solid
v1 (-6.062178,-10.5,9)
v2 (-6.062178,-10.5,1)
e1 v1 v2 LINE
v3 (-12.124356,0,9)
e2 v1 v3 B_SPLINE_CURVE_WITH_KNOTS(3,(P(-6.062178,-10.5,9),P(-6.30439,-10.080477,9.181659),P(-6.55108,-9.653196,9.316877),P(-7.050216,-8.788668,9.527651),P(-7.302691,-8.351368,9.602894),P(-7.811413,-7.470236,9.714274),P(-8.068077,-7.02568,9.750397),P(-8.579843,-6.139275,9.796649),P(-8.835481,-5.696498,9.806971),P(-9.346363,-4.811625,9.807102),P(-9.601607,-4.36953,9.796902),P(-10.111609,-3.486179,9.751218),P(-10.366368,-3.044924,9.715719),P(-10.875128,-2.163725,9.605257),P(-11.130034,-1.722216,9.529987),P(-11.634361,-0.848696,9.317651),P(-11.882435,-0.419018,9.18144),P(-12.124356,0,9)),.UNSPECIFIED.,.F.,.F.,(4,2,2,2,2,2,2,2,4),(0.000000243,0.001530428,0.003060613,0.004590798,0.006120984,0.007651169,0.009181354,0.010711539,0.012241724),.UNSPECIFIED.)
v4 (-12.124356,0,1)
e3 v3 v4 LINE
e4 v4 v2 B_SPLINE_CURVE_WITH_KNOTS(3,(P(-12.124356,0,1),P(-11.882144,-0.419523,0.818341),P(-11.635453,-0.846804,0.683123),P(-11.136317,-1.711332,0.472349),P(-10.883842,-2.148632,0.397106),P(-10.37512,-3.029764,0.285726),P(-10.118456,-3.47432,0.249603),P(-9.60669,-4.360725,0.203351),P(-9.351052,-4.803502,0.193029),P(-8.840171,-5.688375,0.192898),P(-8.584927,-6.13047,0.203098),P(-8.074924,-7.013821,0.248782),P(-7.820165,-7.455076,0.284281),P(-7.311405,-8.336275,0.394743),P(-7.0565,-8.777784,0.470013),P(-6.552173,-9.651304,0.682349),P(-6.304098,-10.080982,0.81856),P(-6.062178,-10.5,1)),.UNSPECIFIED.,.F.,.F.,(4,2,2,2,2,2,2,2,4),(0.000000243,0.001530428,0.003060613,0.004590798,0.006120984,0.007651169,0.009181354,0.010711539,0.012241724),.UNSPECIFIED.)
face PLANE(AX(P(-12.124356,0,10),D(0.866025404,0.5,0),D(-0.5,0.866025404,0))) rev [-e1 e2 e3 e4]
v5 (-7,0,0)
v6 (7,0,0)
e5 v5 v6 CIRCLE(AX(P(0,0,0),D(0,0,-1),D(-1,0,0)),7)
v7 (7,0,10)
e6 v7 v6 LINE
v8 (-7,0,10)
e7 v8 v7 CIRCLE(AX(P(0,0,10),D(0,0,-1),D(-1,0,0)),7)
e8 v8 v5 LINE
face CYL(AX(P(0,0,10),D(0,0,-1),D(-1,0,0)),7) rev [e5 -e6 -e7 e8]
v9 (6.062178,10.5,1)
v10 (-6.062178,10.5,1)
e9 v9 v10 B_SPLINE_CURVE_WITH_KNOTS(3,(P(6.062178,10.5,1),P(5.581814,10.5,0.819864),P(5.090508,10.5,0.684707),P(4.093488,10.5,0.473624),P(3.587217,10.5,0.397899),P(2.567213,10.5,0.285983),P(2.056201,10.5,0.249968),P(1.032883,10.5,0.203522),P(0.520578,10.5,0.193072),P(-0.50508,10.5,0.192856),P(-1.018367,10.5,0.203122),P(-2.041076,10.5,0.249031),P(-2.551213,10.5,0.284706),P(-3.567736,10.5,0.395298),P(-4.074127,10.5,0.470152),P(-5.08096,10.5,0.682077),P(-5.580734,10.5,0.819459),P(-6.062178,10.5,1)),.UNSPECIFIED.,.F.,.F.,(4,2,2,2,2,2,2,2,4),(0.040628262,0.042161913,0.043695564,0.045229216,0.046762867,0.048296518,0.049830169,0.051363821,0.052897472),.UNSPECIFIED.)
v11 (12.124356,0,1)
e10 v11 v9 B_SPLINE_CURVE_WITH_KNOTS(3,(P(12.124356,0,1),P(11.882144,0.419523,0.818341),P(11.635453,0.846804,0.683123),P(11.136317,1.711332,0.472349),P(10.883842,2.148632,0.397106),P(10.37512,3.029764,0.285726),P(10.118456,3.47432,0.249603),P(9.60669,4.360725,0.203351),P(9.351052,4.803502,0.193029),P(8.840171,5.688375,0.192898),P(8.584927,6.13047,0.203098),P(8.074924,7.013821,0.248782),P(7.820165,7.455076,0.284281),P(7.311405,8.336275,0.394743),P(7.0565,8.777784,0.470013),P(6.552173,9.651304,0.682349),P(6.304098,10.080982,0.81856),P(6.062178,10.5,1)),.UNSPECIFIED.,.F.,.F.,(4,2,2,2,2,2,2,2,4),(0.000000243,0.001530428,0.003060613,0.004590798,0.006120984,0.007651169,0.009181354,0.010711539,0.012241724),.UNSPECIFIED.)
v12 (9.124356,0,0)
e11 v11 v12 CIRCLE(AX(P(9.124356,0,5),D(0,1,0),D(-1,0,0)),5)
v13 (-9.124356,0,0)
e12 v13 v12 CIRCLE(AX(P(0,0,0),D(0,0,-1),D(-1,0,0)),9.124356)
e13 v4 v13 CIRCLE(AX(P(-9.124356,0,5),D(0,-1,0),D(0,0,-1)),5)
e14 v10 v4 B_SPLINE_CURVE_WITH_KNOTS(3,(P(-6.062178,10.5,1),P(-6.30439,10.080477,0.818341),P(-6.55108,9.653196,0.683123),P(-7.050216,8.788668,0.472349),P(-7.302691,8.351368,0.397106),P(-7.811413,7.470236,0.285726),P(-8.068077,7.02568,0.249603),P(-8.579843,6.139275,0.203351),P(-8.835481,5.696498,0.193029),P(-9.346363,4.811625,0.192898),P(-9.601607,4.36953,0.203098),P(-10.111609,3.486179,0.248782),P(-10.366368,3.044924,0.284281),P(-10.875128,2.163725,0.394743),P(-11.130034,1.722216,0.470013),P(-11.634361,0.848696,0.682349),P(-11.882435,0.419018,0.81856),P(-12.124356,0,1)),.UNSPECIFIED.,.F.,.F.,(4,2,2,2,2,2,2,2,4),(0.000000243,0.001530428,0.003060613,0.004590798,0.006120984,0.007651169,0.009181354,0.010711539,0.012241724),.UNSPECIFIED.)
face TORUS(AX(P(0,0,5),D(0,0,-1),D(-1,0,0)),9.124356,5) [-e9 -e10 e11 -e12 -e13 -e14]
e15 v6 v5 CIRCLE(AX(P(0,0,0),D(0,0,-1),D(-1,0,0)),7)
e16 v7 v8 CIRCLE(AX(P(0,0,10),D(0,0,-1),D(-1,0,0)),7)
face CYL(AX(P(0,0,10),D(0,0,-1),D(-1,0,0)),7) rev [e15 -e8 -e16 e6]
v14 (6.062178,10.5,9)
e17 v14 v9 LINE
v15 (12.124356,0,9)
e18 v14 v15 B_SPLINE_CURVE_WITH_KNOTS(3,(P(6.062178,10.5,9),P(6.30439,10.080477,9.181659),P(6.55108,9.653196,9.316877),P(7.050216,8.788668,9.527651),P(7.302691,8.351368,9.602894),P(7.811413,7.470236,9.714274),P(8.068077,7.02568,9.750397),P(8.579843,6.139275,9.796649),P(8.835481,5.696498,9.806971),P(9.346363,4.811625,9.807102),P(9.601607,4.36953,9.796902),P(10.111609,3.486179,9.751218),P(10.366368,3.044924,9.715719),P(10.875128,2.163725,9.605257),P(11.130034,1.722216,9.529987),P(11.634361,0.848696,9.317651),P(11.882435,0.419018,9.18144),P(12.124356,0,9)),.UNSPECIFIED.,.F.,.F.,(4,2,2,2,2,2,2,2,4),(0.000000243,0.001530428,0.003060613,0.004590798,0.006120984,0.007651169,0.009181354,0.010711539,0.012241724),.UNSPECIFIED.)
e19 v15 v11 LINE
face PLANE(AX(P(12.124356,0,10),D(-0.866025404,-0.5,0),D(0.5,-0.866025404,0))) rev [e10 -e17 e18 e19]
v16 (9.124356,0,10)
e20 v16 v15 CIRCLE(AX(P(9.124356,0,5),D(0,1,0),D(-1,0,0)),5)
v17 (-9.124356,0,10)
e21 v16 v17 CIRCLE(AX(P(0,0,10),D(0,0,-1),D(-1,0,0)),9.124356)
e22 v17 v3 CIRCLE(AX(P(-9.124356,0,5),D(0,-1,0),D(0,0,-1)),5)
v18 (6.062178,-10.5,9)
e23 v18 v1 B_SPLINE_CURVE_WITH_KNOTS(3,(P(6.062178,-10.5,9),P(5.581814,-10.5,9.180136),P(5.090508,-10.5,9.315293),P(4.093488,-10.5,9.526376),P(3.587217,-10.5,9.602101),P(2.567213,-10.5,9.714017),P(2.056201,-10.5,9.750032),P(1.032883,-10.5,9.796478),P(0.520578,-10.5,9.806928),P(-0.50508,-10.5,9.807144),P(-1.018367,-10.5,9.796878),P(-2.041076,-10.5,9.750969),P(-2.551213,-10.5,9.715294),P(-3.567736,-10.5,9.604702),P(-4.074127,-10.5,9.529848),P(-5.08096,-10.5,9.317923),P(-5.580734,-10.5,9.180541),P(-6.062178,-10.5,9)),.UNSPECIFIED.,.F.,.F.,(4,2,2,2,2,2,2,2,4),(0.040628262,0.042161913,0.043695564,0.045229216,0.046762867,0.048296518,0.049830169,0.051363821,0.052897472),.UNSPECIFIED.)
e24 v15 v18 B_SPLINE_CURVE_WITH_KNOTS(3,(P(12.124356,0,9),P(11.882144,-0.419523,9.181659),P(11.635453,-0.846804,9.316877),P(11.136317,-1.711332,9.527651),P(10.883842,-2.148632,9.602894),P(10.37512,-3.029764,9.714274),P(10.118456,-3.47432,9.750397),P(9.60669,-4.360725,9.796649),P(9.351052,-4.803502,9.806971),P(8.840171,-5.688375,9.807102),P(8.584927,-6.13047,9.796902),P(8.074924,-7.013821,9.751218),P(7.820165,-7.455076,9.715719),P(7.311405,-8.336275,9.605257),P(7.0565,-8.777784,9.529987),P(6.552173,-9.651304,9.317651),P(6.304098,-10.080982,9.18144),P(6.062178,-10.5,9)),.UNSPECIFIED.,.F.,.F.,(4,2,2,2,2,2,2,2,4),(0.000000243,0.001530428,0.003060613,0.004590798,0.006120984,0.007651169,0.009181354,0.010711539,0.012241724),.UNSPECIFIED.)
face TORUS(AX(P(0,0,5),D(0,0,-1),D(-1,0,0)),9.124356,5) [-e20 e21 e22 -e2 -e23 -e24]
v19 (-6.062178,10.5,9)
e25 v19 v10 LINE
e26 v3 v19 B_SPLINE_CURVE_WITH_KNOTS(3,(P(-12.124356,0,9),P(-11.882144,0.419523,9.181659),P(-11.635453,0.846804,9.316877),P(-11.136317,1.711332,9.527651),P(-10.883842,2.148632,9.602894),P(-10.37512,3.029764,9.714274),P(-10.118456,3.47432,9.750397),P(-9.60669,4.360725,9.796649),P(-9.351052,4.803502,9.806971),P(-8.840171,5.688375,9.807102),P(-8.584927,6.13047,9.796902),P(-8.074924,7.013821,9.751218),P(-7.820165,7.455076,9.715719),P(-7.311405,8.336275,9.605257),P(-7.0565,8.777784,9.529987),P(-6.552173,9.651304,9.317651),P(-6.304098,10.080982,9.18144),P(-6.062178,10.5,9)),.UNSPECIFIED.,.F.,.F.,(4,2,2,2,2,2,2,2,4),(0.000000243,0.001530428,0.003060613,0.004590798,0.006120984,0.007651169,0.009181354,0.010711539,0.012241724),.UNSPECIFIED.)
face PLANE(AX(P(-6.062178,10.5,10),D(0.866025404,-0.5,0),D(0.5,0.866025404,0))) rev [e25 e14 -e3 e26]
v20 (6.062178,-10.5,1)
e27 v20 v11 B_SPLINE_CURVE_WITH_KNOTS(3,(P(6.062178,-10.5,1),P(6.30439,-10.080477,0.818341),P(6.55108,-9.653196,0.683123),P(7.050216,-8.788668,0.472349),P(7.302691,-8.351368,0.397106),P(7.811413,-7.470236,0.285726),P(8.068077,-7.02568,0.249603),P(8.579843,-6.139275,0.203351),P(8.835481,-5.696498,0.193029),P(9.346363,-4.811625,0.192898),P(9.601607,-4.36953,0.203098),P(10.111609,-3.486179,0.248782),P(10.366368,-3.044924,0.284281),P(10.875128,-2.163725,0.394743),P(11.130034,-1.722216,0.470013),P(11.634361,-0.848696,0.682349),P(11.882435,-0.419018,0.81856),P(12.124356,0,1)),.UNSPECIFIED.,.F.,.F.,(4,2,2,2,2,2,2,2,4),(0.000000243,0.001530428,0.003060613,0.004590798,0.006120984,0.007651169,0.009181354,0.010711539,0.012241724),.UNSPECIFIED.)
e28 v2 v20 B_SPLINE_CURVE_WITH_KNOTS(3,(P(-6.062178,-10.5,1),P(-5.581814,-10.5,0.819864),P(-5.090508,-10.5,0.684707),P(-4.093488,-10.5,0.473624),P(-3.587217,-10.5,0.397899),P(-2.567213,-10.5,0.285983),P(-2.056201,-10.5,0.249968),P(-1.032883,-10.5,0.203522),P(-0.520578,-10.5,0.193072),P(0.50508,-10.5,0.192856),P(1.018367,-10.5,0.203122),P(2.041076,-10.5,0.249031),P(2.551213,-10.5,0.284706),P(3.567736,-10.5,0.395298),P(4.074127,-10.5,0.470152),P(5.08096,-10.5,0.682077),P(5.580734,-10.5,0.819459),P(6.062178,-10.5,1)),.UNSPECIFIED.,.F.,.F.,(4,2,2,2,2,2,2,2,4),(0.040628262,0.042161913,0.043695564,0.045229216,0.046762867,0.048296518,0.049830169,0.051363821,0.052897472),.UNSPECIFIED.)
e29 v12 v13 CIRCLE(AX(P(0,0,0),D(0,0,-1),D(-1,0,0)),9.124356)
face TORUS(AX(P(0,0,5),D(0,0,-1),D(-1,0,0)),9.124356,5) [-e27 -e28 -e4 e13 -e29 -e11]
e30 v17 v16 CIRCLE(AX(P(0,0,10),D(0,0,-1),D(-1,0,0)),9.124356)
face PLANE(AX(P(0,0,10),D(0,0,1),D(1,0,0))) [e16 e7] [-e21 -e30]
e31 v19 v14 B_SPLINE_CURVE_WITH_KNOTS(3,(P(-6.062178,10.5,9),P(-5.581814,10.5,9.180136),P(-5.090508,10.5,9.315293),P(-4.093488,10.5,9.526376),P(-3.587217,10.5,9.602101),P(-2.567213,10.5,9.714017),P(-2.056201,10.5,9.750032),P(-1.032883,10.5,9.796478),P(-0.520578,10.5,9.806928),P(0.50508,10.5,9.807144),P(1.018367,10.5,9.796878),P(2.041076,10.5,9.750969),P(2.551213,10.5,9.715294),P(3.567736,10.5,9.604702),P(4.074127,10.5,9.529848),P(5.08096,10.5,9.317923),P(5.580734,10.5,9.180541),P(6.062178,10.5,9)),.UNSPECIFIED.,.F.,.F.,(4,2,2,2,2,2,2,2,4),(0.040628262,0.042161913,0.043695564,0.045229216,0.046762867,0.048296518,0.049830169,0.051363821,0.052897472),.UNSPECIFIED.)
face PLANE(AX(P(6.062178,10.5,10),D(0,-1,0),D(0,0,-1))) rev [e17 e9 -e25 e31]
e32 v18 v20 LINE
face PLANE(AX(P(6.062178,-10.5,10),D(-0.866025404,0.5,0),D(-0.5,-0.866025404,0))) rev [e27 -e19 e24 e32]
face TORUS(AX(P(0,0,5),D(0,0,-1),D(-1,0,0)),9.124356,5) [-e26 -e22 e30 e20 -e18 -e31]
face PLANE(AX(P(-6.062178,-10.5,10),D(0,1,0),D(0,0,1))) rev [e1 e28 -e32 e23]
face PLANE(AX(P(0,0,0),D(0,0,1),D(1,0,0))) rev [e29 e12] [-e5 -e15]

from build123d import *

# Parameters (mm, degrees)
BOSS_EXTRUDE1_DEPTH = 10
SKETCH3_R           = 7
CUT_EXTRUDE1_DEPTH  = 10


with BuildPart() as part:
    # Sketch1 → Boss-Extrude1 (new body)
    with BuildSketch(Plane.XY):
        Polygon((12.124355653, 0), (6.062177826, 10.5), (-6.062177826, 10.5), (-12.124355653, 0), (-6.062177826, -10.5), (6.062177826, -10.5), align=None)
    extrude(amount=BOSS_EXTRUDE1_DEPTH)

    # Sketch2 → Cut-Revolve1 (revolve, cut)
    with BuildSketch(Plane(origin=(0, 0, 0), x_dir=(1, 0, 0), z_dir=(0, 1, 0))):
        with BuildLine():
            Line((-12.124355653, 0), (-12.124355653, -1))
            ThreePointArc((-12.124355653, -1), (-10.705494483, -0.25658351), (-9.124355653, 0))
            Line((-9.124355653, 0), (-12.124355653, 0))
        make_face()
        with BuildLine():
            Line((-12.124355653, -10), (-12.124355653, -9))
            ThreePointArc((-12.124355653, -9), (-10.705494483, -9.74341649), (-9.124355653, -10))
            Line((-9.124355653, -10), (-12.124355653, -10))
        make_face()
    revolve(axis=Axis((0, 0, 0), (0, 0, 1)), mode=Mode.SUBTRACT)

    # Sketch3 → Cut-Extrude1 (cut)
    with BuildSketch(Plane(origin=(0, 0, 0), x_dir=(-1, 0, 0), z_dir=(0, 0, -1))):
        Circle(SKETCH3_R)
    extrude(amount=-CUT_EXTRUDE1_DEPTH, mode=Mode.SUBTRACT)


solid = part.part
